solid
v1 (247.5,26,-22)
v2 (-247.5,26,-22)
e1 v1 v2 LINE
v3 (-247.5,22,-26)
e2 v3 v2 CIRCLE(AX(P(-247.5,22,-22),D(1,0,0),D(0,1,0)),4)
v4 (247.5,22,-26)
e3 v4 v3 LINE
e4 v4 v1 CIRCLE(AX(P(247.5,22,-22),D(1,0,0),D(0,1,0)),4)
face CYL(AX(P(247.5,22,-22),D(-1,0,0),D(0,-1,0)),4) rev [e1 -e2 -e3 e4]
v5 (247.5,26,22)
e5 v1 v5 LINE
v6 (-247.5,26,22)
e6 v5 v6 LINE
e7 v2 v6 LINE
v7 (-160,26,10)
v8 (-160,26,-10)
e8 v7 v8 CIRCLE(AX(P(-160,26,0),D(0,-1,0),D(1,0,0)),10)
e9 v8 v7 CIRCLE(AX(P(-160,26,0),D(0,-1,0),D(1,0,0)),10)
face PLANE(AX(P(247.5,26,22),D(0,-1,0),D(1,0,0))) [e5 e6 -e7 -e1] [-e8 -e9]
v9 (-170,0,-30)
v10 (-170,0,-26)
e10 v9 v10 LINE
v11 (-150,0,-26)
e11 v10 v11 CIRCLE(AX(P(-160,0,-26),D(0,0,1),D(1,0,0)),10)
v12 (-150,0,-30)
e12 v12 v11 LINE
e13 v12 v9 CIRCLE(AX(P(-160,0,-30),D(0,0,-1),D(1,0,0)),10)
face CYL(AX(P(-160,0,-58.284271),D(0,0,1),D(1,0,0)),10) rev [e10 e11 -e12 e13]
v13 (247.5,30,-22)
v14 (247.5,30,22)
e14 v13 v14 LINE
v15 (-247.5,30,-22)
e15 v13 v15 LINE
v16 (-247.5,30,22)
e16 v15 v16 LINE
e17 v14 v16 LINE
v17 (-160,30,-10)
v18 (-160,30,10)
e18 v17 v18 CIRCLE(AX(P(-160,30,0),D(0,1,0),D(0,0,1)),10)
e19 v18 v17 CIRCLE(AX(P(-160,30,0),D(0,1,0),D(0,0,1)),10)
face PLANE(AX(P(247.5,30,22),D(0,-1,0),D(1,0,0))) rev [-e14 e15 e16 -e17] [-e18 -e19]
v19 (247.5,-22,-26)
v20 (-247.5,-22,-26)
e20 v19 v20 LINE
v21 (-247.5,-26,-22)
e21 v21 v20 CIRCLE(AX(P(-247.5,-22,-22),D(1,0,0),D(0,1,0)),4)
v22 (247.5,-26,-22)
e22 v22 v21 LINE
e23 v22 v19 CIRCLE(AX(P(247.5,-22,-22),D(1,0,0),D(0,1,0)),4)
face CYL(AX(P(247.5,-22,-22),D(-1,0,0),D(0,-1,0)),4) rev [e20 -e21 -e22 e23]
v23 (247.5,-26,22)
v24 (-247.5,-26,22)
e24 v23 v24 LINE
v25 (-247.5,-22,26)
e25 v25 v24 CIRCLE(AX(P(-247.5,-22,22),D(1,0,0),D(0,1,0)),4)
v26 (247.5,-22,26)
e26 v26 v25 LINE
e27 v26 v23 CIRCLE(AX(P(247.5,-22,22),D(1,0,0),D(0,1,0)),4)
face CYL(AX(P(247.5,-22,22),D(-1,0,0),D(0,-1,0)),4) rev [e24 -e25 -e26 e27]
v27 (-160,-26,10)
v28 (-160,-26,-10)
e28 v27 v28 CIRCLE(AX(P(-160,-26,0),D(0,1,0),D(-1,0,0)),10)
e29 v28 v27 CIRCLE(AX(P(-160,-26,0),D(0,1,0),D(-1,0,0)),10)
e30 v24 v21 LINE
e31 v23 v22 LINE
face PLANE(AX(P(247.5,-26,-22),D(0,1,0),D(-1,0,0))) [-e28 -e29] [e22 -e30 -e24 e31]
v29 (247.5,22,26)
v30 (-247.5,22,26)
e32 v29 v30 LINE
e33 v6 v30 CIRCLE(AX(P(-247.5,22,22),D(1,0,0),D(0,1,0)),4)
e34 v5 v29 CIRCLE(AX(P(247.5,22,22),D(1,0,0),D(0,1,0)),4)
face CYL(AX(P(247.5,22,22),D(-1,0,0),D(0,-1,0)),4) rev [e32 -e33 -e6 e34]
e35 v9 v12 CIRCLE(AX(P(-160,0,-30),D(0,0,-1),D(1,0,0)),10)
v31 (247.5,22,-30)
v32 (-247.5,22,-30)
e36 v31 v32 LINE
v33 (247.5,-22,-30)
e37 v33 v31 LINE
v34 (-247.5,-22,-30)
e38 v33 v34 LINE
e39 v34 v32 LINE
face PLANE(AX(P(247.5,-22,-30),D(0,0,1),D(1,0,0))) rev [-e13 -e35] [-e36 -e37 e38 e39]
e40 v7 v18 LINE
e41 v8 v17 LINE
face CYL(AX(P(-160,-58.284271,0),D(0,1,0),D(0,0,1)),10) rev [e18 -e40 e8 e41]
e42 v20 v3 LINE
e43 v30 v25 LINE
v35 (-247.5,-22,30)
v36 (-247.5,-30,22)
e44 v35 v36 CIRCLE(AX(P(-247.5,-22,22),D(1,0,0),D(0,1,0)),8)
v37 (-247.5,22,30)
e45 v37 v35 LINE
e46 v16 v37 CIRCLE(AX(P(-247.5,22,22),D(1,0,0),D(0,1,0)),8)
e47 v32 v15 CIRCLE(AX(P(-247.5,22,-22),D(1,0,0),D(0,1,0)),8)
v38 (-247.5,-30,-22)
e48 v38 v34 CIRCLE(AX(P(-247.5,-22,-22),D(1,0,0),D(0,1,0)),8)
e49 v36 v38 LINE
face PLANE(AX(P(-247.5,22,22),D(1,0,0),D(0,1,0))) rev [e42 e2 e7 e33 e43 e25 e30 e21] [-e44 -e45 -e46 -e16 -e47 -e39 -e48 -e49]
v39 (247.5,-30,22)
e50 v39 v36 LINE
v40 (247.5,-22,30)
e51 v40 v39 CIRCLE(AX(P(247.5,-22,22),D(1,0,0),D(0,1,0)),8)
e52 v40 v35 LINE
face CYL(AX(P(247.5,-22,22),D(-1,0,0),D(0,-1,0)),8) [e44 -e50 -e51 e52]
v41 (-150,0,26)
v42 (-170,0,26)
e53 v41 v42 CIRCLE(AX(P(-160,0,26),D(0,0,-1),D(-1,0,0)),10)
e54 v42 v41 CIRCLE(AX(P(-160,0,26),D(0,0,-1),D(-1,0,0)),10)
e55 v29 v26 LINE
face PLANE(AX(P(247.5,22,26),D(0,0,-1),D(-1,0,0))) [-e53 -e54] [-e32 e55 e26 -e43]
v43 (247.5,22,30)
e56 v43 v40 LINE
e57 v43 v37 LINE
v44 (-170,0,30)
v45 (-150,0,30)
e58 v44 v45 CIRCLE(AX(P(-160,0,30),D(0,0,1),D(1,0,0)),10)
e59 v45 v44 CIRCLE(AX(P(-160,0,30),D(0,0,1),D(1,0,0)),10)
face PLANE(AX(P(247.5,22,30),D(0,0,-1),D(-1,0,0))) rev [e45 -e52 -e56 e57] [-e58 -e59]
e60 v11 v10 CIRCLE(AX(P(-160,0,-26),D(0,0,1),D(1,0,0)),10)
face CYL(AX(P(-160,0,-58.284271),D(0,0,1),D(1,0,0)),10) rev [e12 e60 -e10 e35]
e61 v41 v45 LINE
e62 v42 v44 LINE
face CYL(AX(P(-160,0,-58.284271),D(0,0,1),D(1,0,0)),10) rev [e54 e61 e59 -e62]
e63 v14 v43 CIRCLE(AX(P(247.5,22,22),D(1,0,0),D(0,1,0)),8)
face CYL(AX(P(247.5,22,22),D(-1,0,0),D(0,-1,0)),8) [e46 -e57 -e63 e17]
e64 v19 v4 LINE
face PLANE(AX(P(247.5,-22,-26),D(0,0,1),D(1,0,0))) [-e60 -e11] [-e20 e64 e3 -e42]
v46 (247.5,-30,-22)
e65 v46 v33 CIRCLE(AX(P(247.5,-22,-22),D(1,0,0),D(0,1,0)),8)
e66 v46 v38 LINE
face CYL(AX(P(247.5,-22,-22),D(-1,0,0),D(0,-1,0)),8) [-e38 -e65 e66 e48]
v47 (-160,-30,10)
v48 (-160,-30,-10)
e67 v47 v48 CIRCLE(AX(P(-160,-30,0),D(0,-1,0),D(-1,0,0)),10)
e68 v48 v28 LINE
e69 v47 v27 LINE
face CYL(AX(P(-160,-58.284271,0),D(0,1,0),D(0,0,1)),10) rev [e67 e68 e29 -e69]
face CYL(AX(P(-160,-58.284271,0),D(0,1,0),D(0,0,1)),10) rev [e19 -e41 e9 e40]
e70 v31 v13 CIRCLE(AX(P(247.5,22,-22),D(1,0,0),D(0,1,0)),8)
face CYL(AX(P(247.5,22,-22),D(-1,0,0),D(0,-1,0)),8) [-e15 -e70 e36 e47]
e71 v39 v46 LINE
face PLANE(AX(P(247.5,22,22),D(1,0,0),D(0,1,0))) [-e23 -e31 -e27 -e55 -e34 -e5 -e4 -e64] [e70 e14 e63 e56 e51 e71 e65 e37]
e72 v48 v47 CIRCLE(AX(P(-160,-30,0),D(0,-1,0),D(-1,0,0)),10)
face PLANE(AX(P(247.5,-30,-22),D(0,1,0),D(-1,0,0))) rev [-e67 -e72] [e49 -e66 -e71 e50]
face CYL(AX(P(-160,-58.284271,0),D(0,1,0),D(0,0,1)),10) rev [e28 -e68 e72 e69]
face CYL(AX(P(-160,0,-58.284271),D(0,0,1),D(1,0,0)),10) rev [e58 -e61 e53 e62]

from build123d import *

# Parameters (mm, degrees)
GB_T6728_2002_60_X_60_X_4_1_DEPTH = 495
CUT_EXTRUDE_1_REACH               = 258.43
SKETCH_5_R                        = 10
CUT_EXTRUDE_2_REACH               = 258.43
SKETCH_6_R                        = 10


with BuildPart() as part:
    # Sketch1 → 冷弯空心方管gb∕t6728-2002 60 X 60 X 4(1) (new body)
    with BuildSketch(Plane.YZ.offset(-247.5)):
        with BuildLine():
            Line((-22, -30), (22, -30))
            ThreePointArc((22, -30), (27.656854249, -27.656854249), (30, -22))
            Line((30, -22), (30, 22))
            ThreePointArc((30, 22), (27.656854249, 27.656854249), (22, 30))
            Line((22, 30), (-22, 30))
            ThreePointArc((-22, 30), (-27.656854249, 27.656854249), (-30, 22))
            Line((-30, 22), (-30, -22))
            ThreePointArc((-30, -22), (-27.656854249, -27.656854249), (-22, -30))
        make_face()
        with BuildLine():
            Line((-22, -26), (22, -26))
            ThreePointArc((22, -26), (24.828427125, -24.828427125), (26, -22))
            Line((26, -22), (26, 22))
            ThreePointArc((26, 22), (24.828427125, 24.828427125), (22, 26))
            Line((22, 26), (-22, 26))
            ThreePointArc((-22, 26), (-24.828427125, 24.828427125), (-26, 22))
            Line((-26, 22), (-26, -22))
            ThreePointArc((-26, -22), (-24.828427125, -24.828427125), (-22, -26))
        make_face(mode=Mode.SUBTRACT)
    extrude(amount=GB_T6728_2002_60_X_60_X_4_1_DEPTH)

    # 切除-拉伸1: up to this face of the body (flat: up to its plane)
    cut_extrude_1_end = Plane(part.part.faces().sort_by_distance((0, 0, -30))[0])
    # 草图5 → 切除-拉伸1 (cut, up to the picked face)
    with BuildSketch(Plane.XY.offset(30), mode=Mode.PRIVATE) as cut_extrude_1_sk1:
        with Locations((-160, 0)):
            Circle(SKETCH_5_R)
    cut_extrude_1_tool1 = split(extrude(cut_extrude_1_sk1.sketch, amount=-CUT_EXTRUDE_1_REACH, mode=Mode.PRIVATE), bisect_by=cut_extrude_1_end, keep=Keep.BOTH, mode=Mode.PRIVATE)
    add(cut_extrude_1_tool1.solids().sort_by(Axis((-160, 0, 30), (0, 0, -1)))[0], mode=Mode.SUBTRACT)

    # 切除-拉伸2: up to this face of the body (flat: up to its plane)
    cut_extrude_2_end = Plane(part.part.faces().sort_by_distance((0, -30, 0))[0])
    # 草图6 → 切除-拉伸2 (cut, up to the picked face)
    with BuildSketch(Plane(origin=(0, 30, 0), x_dir=(1, 0, 0), z_dir=(0, 1, 0)), mode=Mode.PRIVATE) as cut_extrude_2_sk1:
        with Locations(Location((-160, 0, 0), (0, 0, 270))):
            Circle(SKETCH_6_R)
    cut_extrude_2_tool1 = split(extrude(cut_extrude_2_sk1.sketch, amount=-CUT_EXTRUDE_2_REACH, mode=Mode.PRIVATE), bisect_by=cut_extrude_2_end, keep=Keep.BOTH, mode=Mode.PRIVATE)
    add(cut_extrude_2_tool1.solids().sort_by(Axis((-160, 30, 0), (0, -1, 0)))[0], mode=Mode.SUBTRACT)


solid = part.part
